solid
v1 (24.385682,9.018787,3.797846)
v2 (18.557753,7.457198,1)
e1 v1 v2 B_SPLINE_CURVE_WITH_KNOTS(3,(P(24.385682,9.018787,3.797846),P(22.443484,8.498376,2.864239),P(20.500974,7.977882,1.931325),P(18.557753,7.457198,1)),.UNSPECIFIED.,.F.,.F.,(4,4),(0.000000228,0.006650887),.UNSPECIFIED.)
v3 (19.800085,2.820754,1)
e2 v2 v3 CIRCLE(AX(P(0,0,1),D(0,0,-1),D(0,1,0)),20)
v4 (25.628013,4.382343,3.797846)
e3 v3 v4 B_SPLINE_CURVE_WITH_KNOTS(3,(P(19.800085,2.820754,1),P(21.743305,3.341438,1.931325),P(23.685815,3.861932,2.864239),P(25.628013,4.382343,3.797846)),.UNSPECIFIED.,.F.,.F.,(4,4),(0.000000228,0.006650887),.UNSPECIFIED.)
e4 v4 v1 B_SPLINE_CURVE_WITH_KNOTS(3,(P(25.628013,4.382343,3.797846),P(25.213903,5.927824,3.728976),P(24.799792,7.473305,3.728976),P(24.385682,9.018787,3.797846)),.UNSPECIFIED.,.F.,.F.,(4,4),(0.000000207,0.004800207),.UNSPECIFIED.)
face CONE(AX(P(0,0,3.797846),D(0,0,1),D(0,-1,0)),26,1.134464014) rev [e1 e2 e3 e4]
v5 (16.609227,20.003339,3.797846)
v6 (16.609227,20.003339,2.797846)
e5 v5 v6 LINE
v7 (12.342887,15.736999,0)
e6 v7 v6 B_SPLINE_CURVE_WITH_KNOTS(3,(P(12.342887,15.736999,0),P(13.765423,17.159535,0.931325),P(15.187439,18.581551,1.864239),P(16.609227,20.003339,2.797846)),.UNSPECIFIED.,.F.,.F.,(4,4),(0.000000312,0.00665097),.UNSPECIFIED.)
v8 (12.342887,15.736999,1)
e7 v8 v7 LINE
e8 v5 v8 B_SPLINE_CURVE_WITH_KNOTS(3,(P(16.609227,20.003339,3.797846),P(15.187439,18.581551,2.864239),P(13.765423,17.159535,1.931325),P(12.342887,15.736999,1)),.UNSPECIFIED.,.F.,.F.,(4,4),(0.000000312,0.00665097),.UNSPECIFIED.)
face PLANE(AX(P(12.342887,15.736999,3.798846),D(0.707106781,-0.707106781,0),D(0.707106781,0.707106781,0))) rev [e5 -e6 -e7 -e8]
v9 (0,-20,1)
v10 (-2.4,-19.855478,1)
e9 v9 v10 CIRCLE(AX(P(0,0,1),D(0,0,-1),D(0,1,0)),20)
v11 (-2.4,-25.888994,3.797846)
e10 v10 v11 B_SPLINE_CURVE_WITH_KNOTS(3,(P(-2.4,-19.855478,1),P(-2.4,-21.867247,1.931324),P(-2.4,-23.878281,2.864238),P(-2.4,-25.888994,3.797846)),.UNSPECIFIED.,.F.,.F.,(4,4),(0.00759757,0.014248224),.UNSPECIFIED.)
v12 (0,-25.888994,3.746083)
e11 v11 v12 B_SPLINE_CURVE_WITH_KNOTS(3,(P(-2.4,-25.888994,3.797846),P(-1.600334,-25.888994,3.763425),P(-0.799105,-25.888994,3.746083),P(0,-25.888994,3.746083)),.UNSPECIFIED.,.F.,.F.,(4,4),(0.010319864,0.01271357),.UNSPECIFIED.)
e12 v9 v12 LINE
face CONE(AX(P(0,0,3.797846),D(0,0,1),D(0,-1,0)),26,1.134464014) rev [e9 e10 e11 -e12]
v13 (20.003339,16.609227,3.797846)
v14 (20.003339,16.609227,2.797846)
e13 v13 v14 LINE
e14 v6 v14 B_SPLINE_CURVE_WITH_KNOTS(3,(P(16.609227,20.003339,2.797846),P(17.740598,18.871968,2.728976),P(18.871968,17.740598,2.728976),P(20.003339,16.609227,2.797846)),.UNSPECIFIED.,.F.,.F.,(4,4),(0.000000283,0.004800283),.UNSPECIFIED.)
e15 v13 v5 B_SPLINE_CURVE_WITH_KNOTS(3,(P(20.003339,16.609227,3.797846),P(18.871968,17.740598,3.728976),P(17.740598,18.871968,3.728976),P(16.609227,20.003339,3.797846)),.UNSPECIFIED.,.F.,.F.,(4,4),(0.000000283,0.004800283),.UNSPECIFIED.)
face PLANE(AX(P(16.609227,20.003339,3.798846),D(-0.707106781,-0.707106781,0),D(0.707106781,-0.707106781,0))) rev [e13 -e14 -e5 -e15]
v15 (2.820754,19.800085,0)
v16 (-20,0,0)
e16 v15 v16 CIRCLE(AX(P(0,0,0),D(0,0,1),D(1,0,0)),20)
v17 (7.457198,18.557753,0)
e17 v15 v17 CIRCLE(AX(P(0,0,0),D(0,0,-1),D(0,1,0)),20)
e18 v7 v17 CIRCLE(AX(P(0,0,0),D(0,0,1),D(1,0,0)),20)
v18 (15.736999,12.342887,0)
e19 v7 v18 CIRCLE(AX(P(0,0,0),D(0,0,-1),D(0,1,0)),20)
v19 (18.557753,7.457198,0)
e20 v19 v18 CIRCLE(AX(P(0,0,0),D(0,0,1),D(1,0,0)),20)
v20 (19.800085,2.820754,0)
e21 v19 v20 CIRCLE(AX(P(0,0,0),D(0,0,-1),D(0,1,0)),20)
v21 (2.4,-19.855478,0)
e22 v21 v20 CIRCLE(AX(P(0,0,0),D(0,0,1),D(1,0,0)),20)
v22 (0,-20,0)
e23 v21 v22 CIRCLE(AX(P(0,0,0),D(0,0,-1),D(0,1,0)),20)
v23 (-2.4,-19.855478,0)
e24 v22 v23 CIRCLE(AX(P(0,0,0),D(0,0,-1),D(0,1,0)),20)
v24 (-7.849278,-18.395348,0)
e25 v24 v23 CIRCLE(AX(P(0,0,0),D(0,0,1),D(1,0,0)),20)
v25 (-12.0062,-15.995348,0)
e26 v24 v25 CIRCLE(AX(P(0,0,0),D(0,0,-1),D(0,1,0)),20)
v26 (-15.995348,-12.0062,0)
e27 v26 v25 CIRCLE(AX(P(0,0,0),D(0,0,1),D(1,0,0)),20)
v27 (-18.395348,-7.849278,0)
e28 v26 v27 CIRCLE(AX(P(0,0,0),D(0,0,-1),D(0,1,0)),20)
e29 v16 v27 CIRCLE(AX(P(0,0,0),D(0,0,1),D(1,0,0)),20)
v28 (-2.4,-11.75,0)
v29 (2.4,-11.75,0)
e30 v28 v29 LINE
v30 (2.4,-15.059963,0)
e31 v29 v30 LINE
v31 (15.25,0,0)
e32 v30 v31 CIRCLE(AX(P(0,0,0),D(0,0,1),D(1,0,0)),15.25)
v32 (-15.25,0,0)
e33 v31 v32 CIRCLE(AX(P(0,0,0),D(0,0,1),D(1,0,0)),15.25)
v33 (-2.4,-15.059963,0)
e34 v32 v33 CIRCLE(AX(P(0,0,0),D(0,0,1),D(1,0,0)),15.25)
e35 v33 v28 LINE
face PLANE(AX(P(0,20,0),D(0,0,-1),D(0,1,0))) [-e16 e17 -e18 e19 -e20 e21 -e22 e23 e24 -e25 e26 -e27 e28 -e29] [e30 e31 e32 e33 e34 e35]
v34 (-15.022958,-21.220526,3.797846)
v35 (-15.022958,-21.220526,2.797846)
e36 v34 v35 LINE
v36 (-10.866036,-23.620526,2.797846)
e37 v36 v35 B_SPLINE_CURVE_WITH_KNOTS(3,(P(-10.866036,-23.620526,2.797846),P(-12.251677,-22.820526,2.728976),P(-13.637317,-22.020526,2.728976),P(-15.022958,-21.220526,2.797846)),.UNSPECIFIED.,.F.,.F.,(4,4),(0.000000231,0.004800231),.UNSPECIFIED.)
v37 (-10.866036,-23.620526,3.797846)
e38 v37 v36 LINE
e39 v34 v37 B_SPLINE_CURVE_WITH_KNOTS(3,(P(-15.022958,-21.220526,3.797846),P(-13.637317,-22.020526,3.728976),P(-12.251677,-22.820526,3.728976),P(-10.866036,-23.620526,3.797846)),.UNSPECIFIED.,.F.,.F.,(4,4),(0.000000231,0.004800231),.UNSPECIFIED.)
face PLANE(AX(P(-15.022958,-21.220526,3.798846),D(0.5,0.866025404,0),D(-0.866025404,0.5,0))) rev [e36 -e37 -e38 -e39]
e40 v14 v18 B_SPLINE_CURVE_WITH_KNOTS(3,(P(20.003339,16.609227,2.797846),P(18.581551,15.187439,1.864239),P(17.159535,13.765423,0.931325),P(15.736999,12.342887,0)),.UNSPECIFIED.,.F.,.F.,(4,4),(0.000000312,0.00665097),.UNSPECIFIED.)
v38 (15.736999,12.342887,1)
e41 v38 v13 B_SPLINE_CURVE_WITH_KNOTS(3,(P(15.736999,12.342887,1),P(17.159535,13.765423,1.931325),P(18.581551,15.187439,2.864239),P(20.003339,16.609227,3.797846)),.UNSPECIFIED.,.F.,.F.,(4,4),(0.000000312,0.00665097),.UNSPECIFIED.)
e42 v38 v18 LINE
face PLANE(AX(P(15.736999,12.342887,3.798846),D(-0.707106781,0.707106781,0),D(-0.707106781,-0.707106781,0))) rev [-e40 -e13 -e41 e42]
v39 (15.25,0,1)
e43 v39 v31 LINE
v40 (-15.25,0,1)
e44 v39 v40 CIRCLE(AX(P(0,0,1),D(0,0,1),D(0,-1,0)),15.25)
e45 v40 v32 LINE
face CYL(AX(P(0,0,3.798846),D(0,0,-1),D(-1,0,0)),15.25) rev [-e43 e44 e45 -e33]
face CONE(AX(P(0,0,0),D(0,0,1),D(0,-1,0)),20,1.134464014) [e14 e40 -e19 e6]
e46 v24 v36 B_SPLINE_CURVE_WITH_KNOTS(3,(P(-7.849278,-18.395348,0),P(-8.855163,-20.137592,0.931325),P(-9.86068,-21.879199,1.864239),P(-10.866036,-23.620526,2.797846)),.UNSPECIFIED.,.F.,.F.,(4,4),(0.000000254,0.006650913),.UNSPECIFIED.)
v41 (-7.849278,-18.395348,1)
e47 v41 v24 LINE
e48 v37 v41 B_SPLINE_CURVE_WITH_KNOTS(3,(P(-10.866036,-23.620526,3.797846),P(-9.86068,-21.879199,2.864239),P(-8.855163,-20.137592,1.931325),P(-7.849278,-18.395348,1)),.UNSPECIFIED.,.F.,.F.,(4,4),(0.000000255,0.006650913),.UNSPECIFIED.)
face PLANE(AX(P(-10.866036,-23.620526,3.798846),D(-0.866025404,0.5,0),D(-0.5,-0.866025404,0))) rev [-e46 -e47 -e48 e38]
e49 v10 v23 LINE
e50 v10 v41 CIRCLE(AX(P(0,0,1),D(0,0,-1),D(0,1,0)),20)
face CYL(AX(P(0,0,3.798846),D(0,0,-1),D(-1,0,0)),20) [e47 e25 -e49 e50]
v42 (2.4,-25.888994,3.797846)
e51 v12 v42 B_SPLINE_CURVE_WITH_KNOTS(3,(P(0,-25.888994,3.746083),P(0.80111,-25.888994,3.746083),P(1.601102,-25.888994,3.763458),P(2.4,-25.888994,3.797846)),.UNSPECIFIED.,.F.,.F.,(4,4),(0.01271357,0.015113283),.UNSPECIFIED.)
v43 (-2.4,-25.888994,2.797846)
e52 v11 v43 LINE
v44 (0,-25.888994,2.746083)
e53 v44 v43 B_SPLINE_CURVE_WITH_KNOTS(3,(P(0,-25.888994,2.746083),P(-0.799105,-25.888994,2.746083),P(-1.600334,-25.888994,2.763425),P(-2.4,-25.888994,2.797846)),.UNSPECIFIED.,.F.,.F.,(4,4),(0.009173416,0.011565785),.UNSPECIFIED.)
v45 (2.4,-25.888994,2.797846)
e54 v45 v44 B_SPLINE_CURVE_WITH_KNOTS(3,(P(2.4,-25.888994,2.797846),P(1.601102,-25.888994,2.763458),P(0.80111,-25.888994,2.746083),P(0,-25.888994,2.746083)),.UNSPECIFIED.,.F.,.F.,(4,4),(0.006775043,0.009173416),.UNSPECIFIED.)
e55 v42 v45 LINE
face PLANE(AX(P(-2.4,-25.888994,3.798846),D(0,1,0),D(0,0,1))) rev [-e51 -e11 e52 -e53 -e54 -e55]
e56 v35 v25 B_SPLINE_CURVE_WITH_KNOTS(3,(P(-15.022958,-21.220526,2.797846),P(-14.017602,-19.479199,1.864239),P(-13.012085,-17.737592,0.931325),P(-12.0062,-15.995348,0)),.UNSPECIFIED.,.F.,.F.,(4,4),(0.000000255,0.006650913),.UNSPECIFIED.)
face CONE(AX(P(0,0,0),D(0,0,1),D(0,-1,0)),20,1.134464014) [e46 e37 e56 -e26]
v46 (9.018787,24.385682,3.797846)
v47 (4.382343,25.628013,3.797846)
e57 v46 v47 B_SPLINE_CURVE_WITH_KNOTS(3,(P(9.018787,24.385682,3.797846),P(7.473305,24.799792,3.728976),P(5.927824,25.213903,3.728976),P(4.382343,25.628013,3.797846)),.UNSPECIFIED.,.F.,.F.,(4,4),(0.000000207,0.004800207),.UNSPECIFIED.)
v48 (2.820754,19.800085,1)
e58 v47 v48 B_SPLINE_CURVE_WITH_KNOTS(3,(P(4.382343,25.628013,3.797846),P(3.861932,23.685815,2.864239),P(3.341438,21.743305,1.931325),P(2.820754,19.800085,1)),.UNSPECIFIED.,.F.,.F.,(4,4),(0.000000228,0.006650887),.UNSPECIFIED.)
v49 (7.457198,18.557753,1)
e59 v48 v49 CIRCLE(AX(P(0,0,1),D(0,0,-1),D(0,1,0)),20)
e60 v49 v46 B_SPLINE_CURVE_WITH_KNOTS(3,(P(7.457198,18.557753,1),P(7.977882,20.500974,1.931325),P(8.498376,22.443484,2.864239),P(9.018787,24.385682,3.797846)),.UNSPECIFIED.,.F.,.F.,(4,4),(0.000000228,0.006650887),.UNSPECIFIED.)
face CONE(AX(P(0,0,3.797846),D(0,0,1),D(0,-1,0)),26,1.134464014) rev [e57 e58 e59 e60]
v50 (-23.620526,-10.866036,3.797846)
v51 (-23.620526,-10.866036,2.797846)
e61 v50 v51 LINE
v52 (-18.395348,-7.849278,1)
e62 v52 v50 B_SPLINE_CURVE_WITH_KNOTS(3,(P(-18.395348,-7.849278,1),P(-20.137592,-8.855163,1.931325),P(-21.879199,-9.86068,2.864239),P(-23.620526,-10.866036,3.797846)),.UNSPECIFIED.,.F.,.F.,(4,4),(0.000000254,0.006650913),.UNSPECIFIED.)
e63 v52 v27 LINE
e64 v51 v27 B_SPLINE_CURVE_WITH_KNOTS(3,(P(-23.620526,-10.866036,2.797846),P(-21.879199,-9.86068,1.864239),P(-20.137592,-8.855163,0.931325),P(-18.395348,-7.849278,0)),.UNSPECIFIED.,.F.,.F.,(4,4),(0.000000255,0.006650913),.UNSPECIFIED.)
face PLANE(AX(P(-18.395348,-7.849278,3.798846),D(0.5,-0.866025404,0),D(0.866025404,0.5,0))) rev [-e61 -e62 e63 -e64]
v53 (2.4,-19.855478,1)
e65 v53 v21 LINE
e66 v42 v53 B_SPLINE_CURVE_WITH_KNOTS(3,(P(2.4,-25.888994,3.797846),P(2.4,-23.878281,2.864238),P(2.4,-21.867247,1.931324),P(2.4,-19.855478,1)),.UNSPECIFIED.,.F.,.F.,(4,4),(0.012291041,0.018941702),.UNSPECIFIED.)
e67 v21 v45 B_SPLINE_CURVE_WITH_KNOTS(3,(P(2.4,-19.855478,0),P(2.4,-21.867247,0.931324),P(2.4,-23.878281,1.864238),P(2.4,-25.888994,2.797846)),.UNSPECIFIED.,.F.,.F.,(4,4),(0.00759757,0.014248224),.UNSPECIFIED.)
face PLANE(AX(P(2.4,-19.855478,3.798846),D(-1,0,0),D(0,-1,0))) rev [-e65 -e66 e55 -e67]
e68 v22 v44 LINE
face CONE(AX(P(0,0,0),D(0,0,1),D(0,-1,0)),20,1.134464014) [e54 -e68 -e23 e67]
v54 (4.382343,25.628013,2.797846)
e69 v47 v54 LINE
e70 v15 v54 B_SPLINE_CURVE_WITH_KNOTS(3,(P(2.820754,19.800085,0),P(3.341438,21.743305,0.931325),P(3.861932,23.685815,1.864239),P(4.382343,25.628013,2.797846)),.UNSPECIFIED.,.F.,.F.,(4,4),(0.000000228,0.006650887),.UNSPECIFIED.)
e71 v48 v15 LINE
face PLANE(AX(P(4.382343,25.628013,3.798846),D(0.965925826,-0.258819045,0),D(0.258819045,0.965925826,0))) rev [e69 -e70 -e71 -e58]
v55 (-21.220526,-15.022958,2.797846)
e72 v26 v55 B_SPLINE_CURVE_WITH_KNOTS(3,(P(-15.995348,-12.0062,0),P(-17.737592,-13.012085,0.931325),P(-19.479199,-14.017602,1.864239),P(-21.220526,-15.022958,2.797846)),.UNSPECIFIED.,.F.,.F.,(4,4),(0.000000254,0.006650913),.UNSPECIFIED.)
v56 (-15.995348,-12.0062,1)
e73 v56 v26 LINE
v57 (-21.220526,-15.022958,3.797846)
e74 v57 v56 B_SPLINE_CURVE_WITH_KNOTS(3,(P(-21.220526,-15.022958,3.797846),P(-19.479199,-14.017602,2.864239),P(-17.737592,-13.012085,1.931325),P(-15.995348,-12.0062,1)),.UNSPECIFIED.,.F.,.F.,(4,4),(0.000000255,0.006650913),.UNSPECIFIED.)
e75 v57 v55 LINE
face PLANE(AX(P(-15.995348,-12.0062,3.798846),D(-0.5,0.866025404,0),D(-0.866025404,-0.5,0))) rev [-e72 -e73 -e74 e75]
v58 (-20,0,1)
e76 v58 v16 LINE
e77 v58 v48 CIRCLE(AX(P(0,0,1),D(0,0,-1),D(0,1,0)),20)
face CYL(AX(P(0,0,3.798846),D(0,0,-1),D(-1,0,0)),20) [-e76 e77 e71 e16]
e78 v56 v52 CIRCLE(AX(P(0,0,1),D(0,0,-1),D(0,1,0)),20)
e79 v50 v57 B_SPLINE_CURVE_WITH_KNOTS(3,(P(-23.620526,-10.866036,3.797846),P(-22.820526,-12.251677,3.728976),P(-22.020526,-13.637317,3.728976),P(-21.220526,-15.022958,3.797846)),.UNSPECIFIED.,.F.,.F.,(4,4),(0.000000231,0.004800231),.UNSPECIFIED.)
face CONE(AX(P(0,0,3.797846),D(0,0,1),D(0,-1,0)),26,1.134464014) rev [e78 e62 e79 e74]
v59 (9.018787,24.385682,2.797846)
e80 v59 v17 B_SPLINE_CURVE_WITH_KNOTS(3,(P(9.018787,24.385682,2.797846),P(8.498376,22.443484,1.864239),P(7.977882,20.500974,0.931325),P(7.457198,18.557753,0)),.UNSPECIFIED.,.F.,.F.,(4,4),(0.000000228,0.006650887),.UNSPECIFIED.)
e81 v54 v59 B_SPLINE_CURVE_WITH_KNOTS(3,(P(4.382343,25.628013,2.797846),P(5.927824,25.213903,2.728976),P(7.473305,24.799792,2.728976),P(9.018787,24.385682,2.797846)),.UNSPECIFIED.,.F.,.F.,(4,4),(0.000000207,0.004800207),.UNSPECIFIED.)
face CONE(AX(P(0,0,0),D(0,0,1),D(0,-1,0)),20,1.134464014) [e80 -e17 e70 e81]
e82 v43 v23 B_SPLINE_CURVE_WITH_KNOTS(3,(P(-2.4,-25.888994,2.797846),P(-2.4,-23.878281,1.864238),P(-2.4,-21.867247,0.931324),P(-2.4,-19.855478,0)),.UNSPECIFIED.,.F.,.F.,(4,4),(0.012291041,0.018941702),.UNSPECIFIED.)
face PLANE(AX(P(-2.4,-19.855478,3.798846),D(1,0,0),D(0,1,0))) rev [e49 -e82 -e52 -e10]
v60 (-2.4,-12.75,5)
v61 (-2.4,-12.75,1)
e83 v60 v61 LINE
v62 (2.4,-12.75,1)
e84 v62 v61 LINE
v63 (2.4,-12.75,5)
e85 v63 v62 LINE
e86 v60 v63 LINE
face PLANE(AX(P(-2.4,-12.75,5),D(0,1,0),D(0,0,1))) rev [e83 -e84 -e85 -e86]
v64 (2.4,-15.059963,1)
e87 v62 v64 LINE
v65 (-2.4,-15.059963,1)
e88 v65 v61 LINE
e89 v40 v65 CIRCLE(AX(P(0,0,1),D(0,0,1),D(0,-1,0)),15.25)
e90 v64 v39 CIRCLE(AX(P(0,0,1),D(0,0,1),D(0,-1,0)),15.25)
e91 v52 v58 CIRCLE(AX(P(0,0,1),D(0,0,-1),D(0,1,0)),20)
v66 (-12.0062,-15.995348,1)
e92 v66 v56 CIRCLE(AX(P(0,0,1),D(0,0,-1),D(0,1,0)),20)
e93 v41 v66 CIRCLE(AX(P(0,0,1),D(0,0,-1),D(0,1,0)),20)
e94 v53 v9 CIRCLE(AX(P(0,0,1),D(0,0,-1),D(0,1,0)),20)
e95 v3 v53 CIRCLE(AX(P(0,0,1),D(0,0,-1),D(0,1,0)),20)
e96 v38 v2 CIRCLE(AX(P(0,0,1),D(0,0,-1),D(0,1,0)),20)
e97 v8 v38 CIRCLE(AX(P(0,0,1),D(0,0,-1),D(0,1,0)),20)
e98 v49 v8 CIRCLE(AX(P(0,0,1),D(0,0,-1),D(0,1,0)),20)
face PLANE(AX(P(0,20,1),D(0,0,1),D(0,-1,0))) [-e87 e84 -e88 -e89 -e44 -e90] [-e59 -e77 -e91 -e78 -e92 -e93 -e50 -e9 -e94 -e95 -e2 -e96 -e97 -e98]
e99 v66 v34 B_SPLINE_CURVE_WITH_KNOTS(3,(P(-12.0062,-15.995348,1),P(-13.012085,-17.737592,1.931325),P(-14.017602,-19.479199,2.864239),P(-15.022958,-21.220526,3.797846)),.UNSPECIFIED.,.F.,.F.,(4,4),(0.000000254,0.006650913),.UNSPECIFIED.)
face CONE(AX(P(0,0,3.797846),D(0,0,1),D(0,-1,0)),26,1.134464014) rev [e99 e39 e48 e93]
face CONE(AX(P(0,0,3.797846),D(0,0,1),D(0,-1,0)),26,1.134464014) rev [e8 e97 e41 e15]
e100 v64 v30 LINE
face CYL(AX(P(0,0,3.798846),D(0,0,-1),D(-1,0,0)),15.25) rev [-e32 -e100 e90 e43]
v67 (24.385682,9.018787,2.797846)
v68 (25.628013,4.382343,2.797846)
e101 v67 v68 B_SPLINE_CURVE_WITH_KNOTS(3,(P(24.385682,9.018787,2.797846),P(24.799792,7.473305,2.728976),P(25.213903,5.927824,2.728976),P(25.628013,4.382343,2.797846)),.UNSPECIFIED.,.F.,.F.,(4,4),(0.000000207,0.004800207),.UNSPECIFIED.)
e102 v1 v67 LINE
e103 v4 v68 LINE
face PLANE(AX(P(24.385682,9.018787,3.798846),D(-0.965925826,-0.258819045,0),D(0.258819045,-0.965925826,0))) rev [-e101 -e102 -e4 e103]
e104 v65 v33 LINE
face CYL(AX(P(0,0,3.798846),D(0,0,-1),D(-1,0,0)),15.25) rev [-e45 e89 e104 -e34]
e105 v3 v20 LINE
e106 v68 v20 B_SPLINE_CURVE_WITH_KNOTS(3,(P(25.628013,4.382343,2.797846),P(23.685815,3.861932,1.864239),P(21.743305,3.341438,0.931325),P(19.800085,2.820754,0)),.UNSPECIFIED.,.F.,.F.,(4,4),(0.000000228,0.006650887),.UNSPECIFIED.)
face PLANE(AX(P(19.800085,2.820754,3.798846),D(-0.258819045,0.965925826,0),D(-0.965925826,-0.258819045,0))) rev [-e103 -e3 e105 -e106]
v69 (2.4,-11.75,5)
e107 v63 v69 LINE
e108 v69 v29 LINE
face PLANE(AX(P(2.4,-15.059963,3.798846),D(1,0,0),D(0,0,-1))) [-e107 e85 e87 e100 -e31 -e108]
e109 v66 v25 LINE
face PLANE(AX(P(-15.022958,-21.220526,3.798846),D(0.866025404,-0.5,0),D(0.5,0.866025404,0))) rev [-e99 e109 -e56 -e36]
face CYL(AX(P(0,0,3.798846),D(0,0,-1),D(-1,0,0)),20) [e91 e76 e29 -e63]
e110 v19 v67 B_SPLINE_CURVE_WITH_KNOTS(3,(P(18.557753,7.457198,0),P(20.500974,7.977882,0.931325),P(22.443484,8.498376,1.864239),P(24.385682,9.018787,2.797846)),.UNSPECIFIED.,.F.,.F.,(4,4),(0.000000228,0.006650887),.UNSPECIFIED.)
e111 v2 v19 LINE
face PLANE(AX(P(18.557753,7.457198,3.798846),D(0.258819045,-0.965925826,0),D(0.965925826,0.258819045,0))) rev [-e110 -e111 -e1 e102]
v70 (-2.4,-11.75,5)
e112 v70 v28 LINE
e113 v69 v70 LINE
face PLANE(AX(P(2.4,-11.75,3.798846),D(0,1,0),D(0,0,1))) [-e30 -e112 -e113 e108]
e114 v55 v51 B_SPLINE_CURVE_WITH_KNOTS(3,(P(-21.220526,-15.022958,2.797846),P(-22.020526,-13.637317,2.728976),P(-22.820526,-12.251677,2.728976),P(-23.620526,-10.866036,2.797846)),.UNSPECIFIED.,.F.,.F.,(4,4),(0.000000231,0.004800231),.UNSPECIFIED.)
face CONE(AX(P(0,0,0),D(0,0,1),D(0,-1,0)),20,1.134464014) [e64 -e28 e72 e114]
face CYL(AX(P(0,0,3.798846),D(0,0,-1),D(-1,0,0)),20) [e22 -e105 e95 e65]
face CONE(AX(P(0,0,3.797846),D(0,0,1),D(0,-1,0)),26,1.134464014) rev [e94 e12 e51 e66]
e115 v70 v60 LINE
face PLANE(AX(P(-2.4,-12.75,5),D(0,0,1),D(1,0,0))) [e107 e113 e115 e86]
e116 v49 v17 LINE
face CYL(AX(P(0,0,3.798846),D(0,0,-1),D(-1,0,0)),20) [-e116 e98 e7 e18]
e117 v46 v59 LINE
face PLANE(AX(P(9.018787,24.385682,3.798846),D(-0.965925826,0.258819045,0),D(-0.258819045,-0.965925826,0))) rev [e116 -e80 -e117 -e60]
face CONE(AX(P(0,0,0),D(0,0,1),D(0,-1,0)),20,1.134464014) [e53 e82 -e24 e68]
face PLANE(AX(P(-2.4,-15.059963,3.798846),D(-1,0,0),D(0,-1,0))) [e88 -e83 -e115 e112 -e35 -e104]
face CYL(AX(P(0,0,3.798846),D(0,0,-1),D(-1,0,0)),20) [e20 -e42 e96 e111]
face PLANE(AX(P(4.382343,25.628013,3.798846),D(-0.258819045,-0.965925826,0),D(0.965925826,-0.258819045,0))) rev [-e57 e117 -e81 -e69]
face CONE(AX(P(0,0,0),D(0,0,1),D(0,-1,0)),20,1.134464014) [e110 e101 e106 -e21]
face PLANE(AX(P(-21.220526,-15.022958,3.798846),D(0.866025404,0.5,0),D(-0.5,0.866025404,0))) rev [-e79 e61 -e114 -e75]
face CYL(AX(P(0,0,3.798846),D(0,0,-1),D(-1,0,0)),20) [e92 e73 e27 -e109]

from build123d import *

# Parameters (mm, degrees)
SKETCH3_OUTSIDE_W   = 68.728
SKETCH3_OUTSIDE_H   = 68.728
CUT_EXTRUDE2_DEPTH  = 3.797865
SKETCH4_W           = 4.8
SKETCH4_H           = 1
BOSS_EXTRUDE1_DEPTH = 5


with BuildPart() as part:
    # Sketch2 → Base-Revolve (revolve)
    with BuildSketch(Plane(origin=(0, 0, 0), x_dir=(0, 0, -1), z_dir=(1, 0, 0))):
        Polygon((-2.797845949, 26), (0, 20), (0, 0), (-1, 0), (-1, 20), (-3.797845949, 26), align=None)
    revolve(axis=Axis((0, 0, 0), (0, 0, 1)))

    # Sketch3 outside → Cut-Extrude2 (cut)
    # profile 1 of 2: a face of its own
    with BuildSketch(Plane.XY):
        Rectangle(SKETCH3_OUTSIDE_W, SKETCH3_OUTSIDE_H)
        with BuildLine():
            Line((-2.4, -19.855477834), (-2.4, -25.8889938))
            Line((-2.4, -25.8889938), (2.4, -25.8889938))
            Line((2.4, -25.8889938), (2.4, -19.855477834))
            ThreePointArc((2.4, -19.855477834), (15.867066806, -12.17522858), (19.800084541, 2.82075383))
            Line((19.800084541, 2.82075383), (25.628013437, 4.382342671))
            Line((25.628013437, 4.382342671), (24.38568202, 9.018786637))
            Line((24.38568202, 9.018786637), (18.557753125, 7.457197796))
            ThreePointArc((18.557753125, 7.457197796), (17.320508076, 10), (15.736999295, 12.342886745))
            Line((15.736999295, 12.342886745), (20.003339349, 16.6092268))
            Line((20.003339349, 16.6092268), (16.6092268, 20.003339349))
            Line((16.6092268, 20.003339349), (12.342886745, 15.736999295))
            ThreePointArc((12.342886745, 15.736999295), (10, 17.320508076), (7.457197796, 18.557753125))
            Line((7.457197796, 18.557753125), (9.018786637, 24.38568202))
            Line((9.018786637, 24.38568202), (4.382342671, 25.628013437))
            Line((4.382342671, 25.628013437), (2.82075383, 19.800084541))
            ThreePointArc((2.82075383, 19.800084541), (-15.867066806, 12.17522858), (-18.395348208, -7.849277948))
            Line((-18.395348208, -7.849277948), (-23.62052631, -10.866035931))
            Line((-23.62052631, -10.866035931), (-21.22052631, -15.022957869))
            Line((-21.22052631, -15.022957869), (-15.995348208, -12.006199886))
            ThreePointArc((-15.995348208, -12.006199886), (-14.142135624, -14.142135624), (-12.006199886, -15.995348208))
            Line((-12.006199886, -15.995348208), (-15.022957869, -21.22052631))
            Line((-15.022957869, -21.22052631), (-10.866035931, -23.62052631))
            Line((-10.866035931, -23.62052631), (-7.849277948, -18.395348208))
            ThreePointArc((-7.849277948, -18.395348208), (-5.176380902, -19.318516526), (-2.4, -19.855477834))
        make_face(mode=Mode.SUBTRACT)
    # profile 2 of 2: a face of its own
    with BuildSketch(Plane.XY):
        with BuildLine():
            Line((2.4, -15.059963479), (2.4, -11.75))
            Line((2.4, -11.75), (-2.4, -11.75))
            Line((-2.4, -11.75), (-2.4, -15.059963479))
            ThreePointArc((-2.4, -15.059963479), (0, 15.25), (2.4, -15.059963479))
        make_face()
    extrude(amount=CUT_EXTRUDE2_DEPTH, mode=Mode.SUBTRACT)

    # Sketch4 → Boss-Extrude1 (add)
    with BuildSketch(Plane.XY):
        with Locations((0, -12.25)):
            Rectangle(SKETCH4_W, SKETCH4_H)
    extrude(amount=BOSS_EXTRUDE1_DEPTH)


solid = part.part
